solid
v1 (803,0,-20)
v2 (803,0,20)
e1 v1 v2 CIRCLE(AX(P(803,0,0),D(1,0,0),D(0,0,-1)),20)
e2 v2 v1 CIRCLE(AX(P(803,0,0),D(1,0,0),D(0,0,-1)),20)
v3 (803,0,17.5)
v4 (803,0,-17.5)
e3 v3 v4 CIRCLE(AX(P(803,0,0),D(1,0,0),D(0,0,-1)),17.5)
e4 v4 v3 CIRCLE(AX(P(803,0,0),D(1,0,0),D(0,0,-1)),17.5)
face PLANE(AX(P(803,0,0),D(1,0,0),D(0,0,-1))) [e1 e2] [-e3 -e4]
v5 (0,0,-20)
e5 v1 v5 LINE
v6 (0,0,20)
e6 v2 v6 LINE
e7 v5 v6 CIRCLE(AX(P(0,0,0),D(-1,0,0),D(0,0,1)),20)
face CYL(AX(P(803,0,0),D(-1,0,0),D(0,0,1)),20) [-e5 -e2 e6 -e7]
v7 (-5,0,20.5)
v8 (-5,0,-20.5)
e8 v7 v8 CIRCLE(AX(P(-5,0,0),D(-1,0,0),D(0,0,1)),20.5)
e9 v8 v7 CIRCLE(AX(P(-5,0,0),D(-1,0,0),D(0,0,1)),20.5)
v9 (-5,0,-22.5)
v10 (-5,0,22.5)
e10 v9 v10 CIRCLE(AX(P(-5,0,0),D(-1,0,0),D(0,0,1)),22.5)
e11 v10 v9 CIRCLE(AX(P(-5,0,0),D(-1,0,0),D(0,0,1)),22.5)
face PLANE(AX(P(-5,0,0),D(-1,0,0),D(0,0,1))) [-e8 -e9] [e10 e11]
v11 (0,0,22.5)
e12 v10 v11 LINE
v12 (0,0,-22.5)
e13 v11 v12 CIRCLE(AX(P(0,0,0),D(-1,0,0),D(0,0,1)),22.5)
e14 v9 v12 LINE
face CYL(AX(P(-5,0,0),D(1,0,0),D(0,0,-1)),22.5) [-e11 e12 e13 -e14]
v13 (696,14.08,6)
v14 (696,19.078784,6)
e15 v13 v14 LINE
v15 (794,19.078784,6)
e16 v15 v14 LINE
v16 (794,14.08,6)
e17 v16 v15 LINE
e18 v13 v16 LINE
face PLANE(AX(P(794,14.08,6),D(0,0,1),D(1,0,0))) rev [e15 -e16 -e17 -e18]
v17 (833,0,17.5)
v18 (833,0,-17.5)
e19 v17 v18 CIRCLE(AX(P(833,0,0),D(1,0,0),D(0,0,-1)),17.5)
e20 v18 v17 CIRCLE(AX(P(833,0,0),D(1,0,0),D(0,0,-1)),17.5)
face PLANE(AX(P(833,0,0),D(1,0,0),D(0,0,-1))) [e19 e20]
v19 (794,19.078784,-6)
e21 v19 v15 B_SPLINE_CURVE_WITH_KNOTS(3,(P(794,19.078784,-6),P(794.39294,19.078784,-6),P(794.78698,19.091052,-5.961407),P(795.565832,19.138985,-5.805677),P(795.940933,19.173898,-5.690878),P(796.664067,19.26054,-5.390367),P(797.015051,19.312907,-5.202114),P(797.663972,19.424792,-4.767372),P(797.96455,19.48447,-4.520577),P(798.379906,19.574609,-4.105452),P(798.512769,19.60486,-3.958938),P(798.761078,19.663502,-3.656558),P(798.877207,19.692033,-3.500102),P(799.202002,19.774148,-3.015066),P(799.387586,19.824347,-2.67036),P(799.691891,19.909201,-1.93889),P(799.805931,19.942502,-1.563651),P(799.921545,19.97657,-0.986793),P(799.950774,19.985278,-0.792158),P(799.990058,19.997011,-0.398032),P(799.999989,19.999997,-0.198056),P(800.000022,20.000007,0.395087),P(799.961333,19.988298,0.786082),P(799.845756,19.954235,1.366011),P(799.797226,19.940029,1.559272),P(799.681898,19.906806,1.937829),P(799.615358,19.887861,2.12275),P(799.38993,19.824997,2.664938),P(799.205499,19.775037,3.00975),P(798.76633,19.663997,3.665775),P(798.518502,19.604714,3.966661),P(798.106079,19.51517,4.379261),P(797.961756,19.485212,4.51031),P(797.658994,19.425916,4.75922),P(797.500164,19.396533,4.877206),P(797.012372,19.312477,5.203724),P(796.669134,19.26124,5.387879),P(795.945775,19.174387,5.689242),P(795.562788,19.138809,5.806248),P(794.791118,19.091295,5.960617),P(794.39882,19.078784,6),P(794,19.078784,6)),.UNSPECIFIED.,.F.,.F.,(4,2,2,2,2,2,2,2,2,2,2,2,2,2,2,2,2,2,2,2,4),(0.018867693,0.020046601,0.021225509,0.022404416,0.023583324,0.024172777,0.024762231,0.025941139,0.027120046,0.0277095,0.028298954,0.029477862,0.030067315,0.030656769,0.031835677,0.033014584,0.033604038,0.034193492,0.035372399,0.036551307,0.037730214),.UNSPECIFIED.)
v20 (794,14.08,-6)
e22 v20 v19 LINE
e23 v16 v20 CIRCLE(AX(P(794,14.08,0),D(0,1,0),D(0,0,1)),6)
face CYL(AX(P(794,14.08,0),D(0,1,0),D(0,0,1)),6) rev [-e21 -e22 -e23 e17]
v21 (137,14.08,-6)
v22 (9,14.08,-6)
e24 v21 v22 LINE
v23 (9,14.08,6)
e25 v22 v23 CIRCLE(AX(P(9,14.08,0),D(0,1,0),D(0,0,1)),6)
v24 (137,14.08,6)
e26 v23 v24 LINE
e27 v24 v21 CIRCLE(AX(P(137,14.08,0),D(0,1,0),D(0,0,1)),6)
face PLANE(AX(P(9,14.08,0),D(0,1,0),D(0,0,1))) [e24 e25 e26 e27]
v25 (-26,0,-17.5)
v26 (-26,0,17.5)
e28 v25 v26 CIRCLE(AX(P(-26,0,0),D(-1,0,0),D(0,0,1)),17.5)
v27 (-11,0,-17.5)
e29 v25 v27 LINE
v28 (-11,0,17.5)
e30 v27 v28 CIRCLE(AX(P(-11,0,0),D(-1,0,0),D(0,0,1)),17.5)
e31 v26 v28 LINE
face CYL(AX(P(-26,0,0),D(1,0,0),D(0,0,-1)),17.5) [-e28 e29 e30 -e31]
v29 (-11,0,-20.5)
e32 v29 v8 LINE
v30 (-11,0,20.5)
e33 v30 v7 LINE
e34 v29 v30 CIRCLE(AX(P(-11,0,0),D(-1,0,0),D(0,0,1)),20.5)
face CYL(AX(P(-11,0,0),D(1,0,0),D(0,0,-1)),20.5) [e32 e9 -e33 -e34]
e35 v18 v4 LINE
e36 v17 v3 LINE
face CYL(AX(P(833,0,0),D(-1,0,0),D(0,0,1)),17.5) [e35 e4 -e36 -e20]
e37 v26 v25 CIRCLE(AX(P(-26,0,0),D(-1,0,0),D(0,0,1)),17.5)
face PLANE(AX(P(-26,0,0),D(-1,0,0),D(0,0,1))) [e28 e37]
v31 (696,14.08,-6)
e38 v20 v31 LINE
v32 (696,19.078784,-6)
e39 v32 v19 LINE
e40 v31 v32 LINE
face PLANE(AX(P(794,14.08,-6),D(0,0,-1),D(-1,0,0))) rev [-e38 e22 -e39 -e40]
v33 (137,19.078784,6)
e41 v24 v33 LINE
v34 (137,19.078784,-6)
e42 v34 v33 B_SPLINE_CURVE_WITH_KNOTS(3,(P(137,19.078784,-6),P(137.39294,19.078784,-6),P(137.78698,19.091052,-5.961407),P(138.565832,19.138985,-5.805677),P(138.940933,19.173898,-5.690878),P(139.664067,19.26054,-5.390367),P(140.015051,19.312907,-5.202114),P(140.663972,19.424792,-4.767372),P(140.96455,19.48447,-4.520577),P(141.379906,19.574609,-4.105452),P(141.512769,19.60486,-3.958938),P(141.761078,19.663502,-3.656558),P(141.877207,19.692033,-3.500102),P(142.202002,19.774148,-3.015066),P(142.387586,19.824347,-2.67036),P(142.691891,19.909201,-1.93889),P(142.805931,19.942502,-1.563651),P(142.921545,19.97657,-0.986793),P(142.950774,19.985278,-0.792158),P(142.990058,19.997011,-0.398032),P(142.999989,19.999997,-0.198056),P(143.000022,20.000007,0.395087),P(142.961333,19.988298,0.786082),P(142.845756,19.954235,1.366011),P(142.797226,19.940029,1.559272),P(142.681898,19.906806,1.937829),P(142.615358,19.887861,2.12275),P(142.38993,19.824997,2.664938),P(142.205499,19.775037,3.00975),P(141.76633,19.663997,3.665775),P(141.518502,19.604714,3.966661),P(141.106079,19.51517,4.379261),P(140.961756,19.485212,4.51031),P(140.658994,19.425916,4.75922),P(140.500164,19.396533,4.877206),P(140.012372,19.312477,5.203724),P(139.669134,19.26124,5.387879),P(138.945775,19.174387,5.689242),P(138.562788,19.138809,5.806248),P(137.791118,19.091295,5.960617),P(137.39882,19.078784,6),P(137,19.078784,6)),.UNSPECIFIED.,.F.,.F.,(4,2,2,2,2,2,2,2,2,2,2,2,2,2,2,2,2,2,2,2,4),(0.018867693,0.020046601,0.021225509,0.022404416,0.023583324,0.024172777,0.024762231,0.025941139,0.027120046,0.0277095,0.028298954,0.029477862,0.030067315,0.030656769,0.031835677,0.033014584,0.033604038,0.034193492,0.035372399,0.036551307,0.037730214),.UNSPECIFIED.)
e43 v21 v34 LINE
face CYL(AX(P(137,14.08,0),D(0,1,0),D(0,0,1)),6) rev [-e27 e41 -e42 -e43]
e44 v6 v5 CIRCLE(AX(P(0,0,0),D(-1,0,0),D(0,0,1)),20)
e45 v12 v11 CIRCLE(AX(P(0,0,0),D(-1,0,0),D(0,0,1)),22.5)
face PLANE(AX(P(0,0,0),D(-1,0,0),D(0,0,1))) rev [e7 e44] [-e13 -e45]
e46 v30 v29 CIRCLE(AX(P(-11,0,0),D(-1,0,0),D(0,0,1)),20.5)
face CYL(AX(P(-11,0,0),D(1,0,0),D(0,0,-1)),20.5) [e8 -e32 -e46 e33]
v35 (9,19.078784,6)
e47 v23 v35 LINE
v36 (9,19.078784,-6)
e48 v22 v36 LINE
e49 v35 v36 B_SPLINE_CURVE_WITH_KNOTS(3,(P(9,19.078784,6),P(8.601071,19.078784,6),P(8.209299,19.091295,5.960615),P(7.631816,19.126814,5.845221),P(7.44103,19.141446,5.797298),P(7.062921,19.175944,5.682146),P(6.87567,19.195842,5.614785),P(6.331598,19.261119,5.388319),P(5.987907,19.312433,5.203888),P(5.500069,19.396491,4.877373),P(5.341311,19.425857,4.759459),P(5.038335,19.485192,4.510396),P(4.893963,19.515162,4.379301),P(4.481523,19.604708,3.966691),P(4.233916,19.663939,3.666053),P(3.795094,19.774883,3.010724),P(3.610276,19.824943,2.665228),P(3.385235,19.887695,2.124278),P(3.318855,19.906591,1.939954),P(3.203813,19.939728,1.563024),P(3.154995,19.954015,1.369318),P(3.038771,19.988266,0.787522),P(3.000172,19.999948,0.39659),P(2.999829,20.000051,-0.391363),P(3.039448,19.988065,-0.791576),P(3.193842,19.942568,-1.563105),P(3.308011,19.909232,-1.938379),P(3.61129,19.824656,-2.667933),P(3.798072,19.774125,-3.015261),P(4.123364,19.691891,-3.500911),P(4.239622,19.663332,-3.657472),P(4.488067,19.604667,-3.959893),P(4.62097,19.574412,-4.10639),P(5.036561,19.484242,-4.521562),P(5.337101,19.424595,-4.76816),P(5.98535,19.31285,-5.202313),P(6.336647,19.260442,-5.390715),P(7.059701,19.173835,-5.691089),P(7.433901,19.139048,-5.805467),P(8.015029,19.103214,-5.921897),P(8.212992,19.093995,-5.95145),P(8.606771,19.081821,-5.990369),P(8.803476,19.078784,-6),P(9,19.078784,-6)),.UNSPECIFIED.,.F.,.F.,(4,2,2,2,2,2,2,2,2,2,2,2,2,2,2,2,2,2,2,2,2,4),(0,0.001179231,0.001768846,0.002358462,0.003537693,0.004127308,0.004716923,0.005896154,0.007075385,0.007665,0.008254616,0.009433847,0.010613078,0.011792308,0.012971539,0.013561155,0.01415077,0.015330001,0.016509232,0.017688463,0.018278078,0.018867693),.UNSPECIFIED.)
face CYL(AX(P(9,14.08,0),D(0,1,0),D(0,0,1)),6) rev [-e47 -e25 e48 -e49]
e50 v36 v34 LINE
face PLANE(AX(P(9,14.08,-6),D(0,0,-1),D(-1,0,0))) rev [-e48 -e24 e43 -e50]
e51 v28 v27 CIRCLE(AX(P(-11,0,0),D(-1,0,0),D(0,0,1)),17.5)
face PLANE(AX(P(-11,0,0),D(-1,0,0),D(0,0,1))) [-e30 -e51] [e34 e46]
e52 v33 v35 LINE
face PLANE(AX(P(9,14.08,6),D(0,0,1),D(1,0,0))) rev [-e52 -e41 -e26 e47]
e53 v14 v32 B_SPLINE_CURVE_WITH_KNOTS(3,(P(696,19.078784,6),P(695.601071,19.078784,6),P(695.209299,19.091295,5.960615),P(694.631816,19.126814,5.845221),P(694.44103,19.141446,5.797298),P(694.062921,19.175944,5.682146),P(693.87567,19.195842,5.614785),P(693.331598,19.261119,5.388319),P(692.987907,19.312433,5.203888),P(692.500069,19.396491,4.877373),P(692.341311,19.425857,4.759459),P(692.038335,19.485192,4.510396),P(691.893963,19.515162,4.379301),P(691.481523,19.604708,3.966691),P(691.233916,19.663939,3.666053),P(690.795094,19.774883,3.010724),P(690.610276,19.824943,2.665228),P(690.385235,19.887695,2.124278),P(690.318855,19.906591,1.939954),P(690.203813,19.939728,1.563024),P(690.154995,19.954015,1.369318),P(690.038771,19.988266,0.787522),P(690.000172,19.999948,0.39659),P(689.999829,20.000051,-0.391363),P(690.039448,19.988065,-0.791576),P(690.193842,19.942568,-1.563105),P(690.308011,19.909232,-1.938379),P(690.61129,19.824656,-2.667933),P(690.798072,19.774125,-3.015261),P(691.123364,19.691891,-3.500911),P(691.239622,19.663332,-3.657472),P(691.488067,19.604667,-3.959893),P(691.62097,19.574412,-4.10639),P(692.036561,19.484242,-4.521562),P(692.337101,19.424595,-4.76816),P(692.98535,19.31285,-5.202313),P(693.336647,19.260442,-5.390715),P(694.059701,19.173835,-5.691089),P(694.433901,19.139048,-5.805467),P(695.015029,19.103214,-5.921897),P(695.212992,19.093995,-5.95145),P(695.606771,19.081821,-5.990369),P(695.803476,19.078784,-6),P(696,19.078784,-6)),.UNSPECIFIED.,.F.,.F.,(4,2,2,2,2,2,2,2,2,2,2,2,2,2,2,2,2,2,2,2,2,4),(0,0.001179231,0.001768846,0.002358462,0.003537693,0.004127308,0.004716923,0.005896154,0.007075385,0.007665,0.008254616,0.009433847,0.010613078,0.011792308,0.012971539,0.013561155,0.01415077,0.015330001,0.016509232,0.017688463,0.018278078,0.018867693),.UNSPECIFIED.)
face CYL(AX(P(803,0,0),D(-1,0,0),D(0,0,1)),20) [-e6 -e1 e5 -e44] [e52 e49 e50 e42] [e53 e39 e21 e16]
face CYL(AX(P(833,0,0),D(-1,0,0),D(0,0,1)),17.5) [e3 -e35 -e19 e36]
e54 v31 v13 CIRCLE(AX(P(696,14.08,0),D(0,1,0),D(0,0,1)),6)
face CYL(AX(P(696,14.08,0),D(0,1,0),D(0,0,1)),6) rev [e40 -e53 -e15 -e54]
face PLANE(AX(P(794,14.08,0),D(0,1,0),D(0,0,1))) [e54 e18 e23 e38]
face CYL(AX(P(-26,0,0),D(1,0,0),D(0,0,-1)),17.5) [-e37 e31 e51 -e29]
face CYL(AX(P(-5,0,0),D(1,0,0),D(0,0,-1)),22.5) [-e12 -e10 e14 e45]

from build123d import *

# Parameters (mm, degrees)
SKETCH_1_R          = 20
EXTRUDE_1_DEPTH     = 803
SKETCH_2_R          = 17.5
EXTRUDE_2_DEPTH     = 30
SKETCH_3_R          = 22.5
EXTRUDE_3_DEPTH     = 5
SKETCH_4_R          = 20.5
EXTRUDE_4_DEPTH     = 6
EXTRUDE_START       = 15
SKETCH_5_R          = 17.5
EXTRUDE_5_DEPTH     = 15
CUT_EXTRUDE_1_DEPTH = 5.92


with BuildPart() as part:
    # 草图1 → 凸台-拉伸1 (new body)
    with BuildSketch(Plane(origin=(0, 0, 0), x_dir=(0, 0, -1), z_dir=(1, 0, 0))):
        Circle(SKETCH_1_R)
    extrude(amount=EXTRUDE_1_DEPTH)

    # 草图2 → 凸台-拉伸2 (add)
    with BuildSketch(Plane(origin=(803, 0, 0), x_dir=(0, 0, -1), z_dir=(1, 0, 0))):
        Circle(SKETCH_2_R)
    extrude(amount=EXTRUDE_2_DEPTH)

    # 草图3 → 凸台-拉伸3 (add)
    with BuildSketch(Plane.ZY):
        Circle(SKETCH_3_R)
    extrude(amount=EXTRUDE_3_DEPTH)

    # 草图4 → 凸台-拉伸4 (add)
    with BuildSketch(Plane.ZY.offset(5)):
        Circle(SKETCH_4_R)
    extrude(amount=EXTRUDE_4_DEPTH)

    # 草图5 → 凸台-拉伸5 (add)
    with BuildSketch(Plane.ZY.offset(11).offset(EXTRUDE_START)):
        with Locations(Location((0, 0, 0), (0, 0, 180))):
            Circle(SKETCH_5_R)
    extrude(amount=-EXTRUDE_5_DEPTH)

    # 草图6 → 切除-拉伸1 (cut)
    with BuildSketch(Plane(origin=(0, 20, 0), x_dir=(1, 0, 0), z_dir=(0, 1, 0))):
        with BuildLine():
            Line((9, 6), (137, 6))
            ThreePointArc((137, 6), (143, 0), (137, -6))
            Line((137, -6), (9, -6))
            ThreePointArc((9, -6), (3, 0), (9, 6))
        make_face()
        with BuildLine():
            Line((794, -6), (696, -6))
            ThreePointArc((696, -6), (690, 0), (696, 6))
            Line((696, 6), (794, 6))
            ThreePointArc((794, 6), (800, 0), (794, -6))
        make_face()
    extrude(amount=-CUT_EXTRUDE_1_DEPTH, mode=Mode.SUBTRACT)


solid = part.part
